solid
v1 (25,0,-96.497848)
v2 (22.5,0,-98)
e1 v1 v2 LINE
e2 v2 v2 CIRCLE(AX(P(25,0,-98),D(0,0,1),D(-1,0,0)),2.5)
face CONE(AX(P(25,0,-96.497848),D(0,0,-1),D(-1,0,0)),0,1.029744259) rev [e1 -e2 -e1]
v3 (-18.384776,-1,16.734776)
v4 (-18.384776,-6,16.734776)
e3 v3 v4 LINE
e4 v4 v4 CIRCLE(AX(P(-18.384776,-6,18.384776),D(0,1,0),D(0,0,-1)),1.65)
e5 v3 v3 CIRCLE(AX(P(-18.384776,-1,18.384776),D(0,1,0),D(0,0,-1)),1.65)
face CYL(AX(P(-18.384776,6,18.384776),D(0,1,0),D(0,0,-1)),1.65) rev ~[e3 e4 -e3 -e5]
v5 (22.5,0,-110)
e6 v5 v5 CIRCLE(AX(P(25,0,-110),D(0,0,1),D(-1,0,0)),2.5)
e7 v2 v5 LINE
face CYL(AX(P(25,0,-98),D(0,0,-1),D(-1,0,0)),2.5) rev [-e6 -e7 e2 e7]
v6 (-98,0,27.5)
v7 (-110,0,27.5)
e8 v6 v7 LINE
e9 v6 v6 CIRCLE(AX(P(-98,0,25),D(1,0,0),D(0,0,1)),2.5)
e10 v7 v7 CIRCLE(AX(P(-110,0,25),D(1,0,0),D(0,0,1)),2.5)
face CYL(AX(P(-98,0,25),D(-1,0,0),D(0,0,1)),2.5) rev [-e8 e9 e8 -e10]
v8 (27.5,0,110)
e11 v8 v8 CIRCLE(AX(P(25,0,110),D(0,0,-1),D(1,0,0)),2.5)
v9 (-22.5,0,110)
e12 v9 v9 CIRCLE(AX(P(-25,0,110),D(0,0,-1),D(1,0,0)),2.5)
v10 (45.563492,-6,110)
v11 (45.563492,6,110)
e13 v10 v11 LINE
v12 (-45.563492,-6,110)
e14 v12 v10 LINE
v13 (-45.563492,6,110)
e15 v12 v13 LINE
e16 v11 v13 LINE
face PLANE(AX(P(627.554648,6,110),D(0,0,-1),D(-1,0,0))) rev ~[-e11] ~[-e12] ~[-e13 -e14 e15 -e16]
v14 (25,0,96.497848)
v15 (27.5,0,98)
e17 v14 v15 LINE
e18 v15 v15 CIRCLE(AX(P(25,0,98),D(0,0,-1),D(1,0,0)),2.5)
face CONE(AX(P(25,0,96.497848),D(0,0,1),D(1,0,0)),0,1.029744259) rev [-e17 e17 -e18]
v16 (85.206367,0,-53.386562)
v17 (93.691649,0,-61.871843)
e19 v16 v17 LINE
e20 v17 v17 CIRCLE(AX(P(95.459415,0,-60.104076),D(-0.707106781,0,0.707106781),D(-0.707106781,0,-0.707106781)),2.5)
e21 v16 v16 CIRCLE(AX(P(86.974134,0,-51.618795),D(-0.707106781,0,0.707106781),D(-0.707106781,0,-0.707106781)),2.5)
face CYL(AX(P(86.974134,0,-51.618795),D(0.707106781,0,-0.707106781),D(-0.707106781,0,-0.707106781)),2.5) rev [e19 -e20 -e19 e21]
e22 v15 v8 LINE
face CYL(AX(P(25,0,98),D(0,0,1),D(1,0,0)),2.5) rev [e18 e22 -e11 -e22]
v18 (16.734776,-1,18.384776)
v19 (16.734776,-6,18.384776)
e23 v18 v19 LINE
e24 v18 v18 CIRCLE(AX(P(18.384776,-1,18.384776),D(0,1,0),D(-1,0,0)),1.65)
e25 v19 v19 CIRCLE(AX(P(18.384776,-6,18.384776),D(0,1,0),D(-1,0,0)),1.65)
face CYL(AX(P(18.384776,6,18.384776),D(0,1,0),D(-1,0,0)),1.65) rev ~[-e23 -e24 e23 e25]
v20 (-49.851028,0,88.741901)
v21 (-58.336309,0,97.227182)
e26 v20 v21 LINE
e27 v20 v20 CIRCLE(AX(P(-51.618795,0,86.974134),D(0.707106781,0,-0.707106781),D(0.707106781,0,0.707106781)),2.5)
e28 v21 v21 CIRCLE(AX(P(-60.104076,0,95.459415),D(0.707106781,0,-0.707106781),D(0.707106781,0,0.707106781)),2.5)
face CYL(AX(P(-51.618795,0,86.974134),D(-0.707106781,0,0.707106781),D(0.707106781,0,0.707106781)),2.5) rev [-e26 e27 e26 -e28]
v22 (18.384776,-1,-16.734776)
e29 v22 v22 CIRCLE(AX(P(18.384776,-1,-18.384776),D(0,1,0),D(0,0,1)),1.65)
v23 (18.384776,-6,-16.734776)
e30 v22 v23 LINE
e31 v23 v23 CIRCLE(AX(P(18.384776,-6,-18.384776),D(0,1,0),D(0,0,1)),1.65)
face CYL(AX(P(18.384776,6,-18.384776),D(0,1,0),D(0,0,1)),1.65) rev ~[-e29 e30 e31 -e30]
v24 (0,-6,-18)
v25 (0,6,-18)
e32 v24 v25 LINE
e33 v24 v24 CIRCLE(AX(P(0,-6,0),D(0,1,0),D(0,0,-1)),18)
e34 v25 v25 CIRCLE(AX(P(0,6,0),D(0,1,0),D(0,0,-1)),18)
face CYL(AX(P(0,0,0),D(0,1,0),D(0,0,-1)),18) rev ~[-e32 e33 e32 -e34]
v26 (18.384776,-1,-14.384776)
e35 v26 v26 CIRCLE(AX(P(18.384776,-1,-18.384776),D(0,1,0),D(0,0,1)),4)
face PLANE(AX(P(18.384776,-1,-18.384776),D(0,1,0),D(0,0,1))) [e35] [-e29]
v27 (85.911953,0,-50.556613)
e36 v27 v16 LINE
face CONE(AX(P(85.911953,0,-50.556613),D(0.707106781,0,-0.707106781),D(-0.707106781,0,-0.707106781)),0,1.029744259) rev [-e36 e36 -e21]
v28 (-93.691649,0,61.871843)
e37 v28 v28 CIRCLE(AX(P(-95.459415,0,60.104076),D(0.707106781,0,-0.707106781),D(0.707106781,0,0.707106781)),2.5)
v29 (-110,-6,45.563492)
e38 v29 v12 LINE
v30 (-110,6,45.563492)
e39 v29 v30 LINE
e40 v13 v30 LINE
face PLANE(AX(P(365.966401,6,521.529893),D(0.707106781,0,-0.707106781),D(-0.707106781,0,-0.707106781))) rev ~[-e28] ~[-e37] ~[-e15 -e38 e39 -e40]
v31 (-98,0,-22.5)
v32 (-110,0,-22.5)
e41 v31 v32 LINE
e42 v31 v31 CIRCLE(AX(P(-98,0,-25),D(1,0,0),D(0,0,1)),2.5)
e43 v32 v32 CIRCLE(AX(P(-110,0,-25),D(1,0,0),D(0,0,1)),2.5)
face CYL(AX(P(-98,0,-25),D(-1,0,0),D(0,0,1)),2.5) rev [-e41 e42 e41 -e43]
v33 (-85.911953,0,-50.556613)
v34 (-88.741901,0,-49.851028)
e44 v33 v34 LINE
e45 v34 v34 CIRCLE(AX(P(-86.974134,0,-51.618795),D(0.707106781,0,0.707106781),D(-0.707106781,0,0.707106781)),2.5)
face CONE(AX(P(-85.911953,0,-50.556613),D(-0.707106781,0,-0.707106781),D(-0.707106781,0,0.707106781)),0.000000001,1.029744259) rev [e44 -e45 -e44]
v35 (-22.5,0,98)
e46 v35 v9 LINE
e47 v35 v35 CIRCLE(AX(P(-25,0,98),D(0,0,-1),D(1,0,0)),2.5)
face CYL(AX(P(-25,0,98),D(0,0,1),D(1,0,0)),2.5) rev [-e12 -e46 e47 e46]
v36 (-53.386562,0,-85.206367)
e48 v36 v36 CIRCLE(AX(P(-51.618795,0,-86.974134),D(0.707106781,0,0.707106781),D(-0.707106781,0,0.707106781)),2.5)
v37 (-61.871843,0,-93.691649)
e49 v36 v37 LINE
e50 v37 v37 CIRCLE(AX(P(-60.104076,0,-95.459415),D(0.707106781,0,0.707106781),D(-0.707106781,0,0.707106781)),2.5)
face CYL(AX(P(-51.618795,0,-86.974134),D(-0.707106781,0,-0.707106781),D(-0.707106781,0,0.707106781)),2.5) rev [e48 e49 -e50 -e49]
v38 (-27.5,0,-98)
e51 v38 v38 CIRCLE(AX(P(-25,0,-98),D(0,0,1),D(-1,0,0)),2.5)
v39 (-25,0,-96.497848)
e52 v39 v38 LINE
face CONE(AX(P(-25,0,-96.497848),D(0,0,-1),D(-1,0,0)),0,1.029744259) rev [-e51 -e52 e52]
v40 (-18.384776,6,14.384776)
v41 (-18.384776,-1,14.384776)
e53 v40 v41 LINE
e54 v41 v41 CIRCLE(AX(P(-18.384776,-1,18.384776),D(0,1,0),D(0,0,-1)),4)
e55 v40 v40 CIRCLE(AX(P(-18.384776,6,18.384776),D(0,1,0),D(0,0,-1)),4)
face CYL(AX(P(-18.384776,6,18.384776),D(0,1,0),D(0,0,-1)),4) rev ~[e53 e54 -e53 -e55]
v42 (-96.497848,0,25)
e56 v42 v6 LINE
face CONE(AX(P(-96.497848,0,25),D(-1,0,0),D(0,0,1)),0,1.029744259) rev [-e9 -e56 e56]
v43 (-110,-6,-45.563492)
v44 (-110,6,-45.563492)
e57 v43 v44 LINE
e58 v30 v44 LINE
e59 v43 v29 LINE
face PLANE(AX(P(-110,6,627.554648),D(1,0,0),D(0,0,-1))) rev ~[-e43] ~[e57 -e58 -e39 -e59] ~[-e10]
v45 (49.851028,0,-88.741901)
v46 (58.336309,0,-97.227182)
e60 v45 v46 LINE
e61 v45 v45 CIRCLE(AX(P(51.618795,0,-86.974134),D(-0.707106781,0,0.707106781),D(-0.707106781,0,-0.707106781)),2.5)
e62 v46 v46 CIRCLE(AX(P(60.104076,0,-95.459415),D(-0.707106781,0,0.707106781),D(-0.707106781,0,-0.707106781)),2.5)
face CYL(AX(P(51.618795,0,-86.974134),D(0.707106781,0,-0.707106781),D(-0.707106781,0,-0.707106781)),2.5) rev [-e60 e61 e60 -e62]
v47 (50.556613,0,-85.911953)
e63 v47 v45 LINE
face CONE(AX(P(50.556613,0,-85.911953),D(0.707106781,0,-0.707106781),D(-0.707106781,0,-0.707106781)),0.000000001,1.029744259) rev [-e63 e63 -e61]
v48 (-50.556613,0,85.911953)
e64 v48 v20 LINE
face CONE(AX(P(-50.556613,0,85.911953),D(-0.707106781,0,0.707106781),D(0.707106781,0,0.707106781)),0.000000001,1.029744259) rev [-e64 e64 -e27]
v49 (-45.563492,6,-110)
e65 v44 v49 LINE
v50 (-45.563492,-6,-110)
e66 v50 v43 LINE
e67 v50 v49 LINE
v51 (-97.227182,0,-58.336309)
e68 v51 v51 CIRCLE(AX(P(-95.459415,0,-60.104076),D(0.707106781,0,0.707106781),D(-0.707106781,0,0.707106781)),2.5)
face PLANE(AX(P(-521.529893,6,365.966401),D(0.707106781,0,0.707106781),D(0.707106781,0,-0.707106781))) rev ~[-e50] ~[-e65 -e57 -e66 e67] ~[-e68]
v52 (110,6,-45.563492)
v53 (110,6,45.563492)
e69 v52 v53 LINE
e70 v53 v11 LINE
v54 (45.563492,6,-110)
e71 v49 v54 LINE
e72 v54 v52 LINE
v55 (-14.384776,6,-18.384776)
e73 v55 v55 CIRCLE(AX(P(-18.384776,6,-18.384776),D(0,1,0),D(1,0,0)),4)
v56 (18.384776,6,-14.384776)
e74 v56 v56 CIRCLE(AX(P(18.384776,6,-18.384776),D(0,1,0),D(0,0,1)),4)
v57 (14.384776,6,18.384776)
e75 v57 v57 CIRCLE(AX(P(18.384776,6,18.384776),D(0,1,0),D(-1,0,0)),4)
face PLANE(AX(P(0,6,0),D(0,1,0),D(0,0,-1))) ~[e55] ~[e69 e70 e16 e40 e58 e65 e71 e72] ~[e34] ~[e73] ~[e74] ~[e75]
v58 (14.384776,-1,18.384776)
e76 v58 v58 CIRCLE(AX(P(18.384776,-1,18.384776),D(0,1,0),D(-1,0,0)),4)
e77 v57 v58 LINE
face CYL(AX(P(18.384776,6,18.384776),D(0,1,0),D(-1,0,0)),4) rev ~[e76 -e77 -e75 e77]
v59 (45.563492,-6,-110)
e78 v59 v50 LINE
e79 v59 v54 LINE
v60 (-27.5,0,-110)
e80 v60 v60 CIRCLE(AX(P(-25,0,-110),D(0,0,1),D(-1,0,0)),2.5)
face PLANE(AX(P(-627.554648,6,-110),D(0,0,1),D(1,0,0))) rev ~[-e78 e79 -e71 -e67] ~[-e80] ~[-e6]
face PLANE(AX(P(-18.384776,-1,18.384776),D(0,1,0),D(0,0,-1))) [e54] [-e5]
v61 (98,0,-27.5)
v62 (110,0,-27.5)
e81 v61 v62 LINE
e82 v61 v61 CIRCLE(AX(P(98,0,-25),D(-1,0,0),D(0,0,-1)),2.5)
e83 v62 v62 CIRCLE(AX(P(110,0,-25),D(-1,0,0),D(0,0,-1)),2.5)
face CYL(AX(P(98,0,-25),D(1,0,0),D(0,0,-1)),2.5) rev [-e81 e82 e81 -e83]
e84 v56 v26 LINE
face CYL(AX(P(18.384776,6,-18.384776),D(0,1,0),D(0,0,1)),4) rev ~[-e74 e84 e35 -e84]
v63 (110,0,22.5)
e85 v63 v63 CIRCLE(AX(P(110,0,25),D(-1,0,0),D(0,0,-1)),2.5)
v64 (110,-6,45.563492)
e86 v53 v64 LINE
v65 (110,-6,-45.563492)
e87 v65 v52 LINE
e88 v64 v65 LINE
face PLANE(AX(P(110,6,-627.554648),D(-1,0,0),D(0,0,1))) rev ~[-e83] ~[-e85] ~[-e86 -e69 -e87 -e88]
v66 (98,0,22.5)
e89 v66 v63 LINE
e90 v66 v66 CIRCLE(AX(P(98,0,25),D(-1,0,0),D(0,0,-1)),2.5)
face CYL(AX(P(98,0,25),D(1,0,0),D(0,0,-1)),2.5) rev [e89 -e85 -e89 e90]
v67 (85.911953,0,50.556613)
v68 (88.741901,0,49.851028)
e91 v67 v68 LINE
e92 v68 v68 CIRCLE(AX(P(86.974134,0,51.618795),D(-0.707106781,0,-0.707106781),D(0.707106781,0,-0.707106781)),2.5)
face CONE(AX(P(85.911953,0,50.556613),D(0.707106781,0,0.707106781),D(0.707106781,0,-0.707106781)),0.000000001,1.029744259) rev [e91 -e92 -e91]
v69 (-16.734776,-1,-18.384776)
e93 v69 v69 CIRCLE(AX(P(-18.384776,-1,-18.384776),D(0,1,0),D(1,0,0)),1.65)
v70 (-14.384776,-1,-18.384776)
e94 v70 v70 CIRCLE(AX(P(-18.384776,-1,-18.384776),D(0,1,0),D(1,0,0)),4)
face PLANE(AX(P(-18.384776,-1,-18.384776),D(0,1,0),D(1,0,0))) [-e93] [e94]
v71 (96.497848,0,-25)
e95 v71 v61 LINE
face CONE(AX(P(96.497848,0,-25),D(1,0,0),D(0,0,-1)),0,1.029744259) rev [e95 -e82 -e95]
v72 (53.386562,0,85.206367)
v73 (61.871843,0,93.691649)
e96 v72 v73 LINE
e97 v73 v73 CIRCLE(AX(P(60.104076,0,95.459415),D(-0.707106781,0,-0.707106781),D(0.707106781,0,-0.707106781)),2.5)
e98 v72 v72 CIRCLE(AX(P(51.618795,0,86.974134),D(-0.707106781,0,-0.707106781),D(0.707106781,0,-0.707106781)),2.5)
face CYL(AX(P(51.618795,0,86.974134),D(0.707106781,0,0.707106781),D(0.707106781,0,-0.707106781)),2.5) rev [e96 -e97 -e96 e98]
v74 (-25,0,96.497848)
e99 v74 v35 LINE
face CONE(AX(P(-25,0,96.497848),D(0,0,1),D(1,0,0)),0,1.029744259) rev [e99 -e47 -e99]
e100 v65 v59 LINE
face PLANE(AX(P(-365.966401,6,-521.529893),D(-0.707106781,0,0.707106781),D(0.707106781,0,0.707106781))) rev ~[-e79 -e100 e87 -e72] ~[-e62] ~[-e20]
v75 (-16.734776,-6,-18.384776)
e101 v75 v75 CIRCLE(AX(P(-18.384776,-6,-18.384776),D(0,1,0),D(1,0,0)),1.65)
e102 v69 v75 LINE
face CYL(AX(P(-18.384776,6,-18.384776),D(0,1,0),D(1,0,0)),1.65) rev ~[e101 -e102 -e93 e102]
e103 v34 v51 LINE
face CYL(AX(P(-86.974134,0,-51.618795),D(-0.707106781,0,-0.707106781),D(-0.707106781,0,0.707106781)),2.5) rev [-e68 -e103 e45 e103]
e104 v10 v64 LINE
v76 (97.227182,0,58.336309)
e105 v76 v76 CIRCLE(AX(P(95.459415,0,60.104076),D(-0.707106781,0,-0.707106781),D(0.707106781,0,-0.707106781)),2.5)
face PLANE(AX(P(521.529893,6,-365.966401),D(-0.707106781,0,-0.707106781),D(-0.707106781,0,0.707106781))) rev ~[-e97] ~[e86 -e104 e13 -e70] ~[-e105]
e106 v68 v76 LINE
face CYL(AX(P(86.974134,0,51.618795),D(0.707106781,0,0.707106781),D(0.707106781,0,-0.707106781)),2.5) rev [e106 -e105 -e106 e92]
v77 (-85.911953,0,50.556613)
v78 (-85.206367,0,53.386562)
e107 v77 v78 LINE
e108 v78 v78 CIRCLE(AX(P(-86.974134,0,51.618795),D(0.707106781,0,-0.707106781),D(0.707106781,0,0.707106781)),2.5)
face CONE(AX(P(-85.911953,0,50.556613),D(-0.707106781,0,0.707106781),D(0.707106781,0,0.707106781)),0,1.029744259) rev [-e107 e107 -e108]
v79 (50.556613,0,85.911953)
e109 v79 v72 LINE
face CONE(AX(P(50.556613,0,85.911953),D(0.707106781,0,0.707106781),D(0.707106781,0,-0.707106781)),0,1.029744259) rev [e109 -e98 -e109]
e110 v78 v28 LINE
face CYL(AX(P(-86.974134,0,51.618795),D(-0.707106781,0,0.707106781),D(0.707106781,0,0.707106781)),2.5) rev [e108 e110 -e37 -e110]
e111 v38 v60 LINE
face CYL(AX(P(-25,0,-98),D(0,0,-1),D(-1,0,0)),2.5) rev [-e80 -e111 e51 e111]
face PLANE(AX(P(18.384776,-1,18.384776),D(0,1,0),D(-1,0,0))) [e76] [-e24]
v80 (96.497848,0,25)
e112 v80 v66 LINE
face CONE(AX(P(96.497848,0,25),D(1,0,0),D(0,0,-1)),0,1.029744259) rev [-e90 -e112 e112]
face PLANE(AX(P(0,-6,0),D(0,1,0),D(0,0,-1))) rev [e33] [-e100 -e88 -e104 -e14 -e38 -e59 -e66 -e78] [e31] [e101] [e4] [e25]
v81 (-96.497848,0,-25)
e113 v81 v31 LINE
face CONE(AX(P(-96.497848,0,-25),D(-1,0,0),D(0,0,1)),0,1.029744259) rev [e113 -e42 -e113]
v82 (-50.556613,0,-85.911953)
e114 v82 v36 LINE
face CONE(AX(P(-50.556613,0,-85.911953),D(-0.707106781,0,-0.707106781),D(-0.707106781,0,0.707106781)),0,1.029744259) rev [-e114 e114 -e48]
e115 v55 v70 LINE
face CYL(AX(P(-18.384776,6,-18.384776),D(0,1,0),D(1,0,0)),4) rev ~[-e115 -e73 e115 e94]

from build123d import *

# Parameters (mm, degrees)
SKETCH_1_W               = 102
SKETCH_1_H               = 12
CUT_EXTRUDE_1_DEPTH      = 83
M6X1_0_1_AT_2_COUNT      = 2
M6X1_0_1_AT_2_PITCH      = 50
PATTERN_CIRCULAR_1_COUNT = 8
SKETCH_7_R               = 1.65
CUT_EXTRUDE_2_DEPTH      = 30
SKETCH_8_R               = 4
CUT_EXTRUDE_3_DEPTH      = 7
PATTERN_CIRCULAR_2_COUNT = 4


with BuildPart() as part:
    # 草图1 → 旋转1 (revolve)
    with BuildSketch(Plane.XY, mode=Mode.PRIVATE) as revolve_1_sk:
        with Locations((69, 0)):
            Rectangle(SKETCH_1_W, SKETCH_1_H)
    revolve(revolve_1_sk.sketch.rotate(Axis((0, 0, 0), (0, 1, 0)), 90), axis=Axis((0, 0, 0), (0, 1, 0)))

    # 草图4 → 切除-拉伸1 (cut)
    with BuildSketch(Plane(origin=(0, 6, 0), x_dir=(1, 0, 0), z_dir=(0, 1, 0))):
        Polygon((110, 627.554648283), (110, 47.958315233), (110, -47.958315233), (110, -627.554648283), (1269.1926661, -627.554648283), (1269.1926661, 627.554648283), align=None)
    cut_extrude_1 = extrude(amount=-CUT_EXTRUDE_1_DEPTH, mode=Mode.SUBTRACT)

    # 草图6 → M6x1.0 螺纹孔1 (revolve, cut)
    with BuildSketch(Plane(origin=(110, 0, 25), x_dir=(0, 0, -1), z_dir=(0, 1, 0))):
        Polygon((0, 0), (0, 13.502151548), (2.5, 12), (2.5, 0), align=None)
    m6x1_0_1 = revolve(axis=Axis((116.35, 0, 25), (-1, 0, 0)), mode=Mode.SUBTRACT)

    # M6x1.0 螺纹孔1 at 2: M6x1.0 螺纹孔1 ×2
    with Locations(*[(0, 0, -i * M6X1_0_1_AT_2_PITCH) for i in range(1, M6X1_0_1_AT_2_COUNT)]):
        add(m6x1_0_1, mode=Mode.SUBTRACT)

    # 阵列(圆周)1: 切除-拉伸1, M6x1.0 螺纹孔1 ×8 about axis
    pattern_circular_1_axis = Axis((0, 0, 0), (0, 1, 0))
    add([cut_extrude_1.rotate(pattern_circular_1_axis, i * 360 / PATTERN_CIRCULAR_1_COUNT) for i in range(1, PATTERN_CIRCULAR_1_COUNT)], mode=Mode.SUBTRACT)
    add([m6x1_0_1.rotate(pattern_circular_1_axis, i * 360 / PATTERN_CIRCULAR_1_COUNT) for i in range(1, PATTERN_CIRCULAR_1_COUNT)], mode=Mode.SUBTRACT)

    # 阵列(圆周)1 copy 1 sketch → 阵列(圆周)1 copy 1 (revolve, cut)
    with BuildSketch(Plane(origin=(60.104076401, 0, -95.45941546), x_dir=(-0.7071067811865475, 0, -0.7071067811865476), z_dir=(0, 1, 0))):
        Polygon((0, 0), (0, 13.502151548), (2.5, 12), (2.5, 0), align=None)
    revolve(axis=Axis((64.594204461, 0, -99.949543521), (-0.7071067811865476, 0, 0.7071067811865475)), mode=Mode.SUBTRACT)

    # 阵列(圆周)1 copy 2 sketch → 阵列(圆周)1 copy 2 (revolve, cut)
    with BuildSketch(Plane(origin=(-25, 0, -110), x_dir=(-1, 0, 0), z_dir=(0, 1, 0))):
        Polygon((0, 0), (0, 13.502151548), (2.5, 12), (2.5, 0), align=None)
    revolve(axis=Axis((-25, 0, -116.35), (0, 0, 1)), mode=Mode.SUBTRACT)

    # 阵列(圆周)1 copy 3 sketch → 阵列(圆周)1 copy 3 (revolve, cut)
    with BuildSketch(Plane(origin=(-95.45941546, 0, -60.104076401), x_dir=(-0.7071067811865476, 0, 0.7071067811865475), z_dir=(0, 1, 0))):
        Polygon((0, 0), (0, 13.502151548), (2.5, 12), (2.5, 0), align=None)
    revolve(axis=Axis((-99.949543521, 0, -64.594204461), (0.7071067811865475, 0, 0.7071067811865476)), mode=Mode.SUBTRACT)

    # 阵列(圆周)1 copy 4 sketch → 阵列(圆周)1 copy 4 (revolve, cut)
    with BuildSketch(Plane(origin=(-110, 0, 25), x_dir=(0, 0, 1), z_dir=(0, 1, 0))):
        Polygon((0, 0), (0, 13.502151548), (2.5, 12), (2.5, 0), align=None)
    revolve(axis=Axis((-116.35, 0, 25), (1, 0, 0)), mode=Mode.SUBTRACT)

    # 阵列(圆周)1 copy 5 sketch → 阵列(圆周)1 copy 5 (revolve, cut)
    with BuildSketch(Plane(origin=(-60.104076401, 0, 95.45941546), x_dir=(0.7071067811865475, 0, 0.7071067811865477), z_dir=(0, 1, 0))):
        Polygon((0, 0), (0, 13.502151548), (2.5, 12), (2.5, 0), align=None)
    revolve(axis=Axis((-64.594204461, 0, 99.949543521), (0.7071067811865477, 0, -0.7071067811865475)), mode=Mode.SUBTRACT)

    # 阵列(圆周)1 copy 6 sketch → 阵列(圆周)1 copy 6 (revolve, cut)
    with BuildSketch(Plane(origin=(25, 0, 110), x_dir=(1, 0, 0), z_dir=(0, 1, 0))):
        Polygon((0, 0), (0, 13.502151548), (2.5, 12), (2.5, 0), align=None)
    revolve(axis=Axis((25, 0, 116.35), (0, 0, -1)), mode=Mode.SUBTRACT)

    # 阵列(圆周)1 copy 7 sketch → 阵列(圆周)1 copy 7 (revolve, cut)
    with BuildSketch(Plane(origin=(95.45941546, 0, 60.104076401), x_dir=(0.7071067811865477, 0, -0.7071067811865474), z_dir=(0, 1, 0))):
        Polygon((0, 0), (0, 13.502151548), (2.5, 12), (2.5, 0), align=None)
    revolve(axis=Axis((99.949543521, 0, 64.594204461), (-0.7071067811865474, 0, -0.7071067811865477)), mode=Mode.SUBTRACT)

    # 草图7 → 切除-拉伸2 (cut)
    with BuildSketch(Plane(origin=(0, 6, 0), x_dir=(1, 0, 0), z_dir=(0, 1, 0))):
        with Locations(Location((18.384776311, 18.384776311, 0), (0, 0, 270))):
            Circle(SKETCH_7_R)
    cut_extrude_2 = extrude(amount=-CUT_EXTRUDE_2_DEPTH, mode=Mode.SUBTRACT)

    # 草图8 → 切除-拉伸3 (cut)
    with BuildSketch(Plane(origin=(0, 6, 0), x_dir=(1, 0, 0), z_dir=(0, 1, 0))):
        with Locations(Location((18.384776311, 18.384776311, 0), (0, 0, 270))):
            Circle(SKETCH_8_R)
    cut_extrude_3 = extrude(amount=-CUT_EXTRUDE_3_DEPTH, mode=Mode.SUBTRACT)

    # 阵列(圆周)2: 切除-拉伸2, 切除-拉伸3 ×4 about axis
    pattern_circular_2_axis = Axis((0, 0, 0), (0, 1, 0))
    add([cut_extrude_2.rotate(pattern_circular_2_axis, i * 360 / PATTERN_CIRCULAR_2_COUNT) for i in range(1, PATTERN_CIRCULAR_2_COUNT)], mode=Mode.SUBTRACT)
    add([cut_extrude_3.rotate(pattern_circular_2_axis, i * 360 / PATTERN_CIRCULAR_2_COUNT) for i in range(1, PATTERN_CIRCULAR_2_COUNT)], mode=Mode.SUBTRACT)


solid = part.part
